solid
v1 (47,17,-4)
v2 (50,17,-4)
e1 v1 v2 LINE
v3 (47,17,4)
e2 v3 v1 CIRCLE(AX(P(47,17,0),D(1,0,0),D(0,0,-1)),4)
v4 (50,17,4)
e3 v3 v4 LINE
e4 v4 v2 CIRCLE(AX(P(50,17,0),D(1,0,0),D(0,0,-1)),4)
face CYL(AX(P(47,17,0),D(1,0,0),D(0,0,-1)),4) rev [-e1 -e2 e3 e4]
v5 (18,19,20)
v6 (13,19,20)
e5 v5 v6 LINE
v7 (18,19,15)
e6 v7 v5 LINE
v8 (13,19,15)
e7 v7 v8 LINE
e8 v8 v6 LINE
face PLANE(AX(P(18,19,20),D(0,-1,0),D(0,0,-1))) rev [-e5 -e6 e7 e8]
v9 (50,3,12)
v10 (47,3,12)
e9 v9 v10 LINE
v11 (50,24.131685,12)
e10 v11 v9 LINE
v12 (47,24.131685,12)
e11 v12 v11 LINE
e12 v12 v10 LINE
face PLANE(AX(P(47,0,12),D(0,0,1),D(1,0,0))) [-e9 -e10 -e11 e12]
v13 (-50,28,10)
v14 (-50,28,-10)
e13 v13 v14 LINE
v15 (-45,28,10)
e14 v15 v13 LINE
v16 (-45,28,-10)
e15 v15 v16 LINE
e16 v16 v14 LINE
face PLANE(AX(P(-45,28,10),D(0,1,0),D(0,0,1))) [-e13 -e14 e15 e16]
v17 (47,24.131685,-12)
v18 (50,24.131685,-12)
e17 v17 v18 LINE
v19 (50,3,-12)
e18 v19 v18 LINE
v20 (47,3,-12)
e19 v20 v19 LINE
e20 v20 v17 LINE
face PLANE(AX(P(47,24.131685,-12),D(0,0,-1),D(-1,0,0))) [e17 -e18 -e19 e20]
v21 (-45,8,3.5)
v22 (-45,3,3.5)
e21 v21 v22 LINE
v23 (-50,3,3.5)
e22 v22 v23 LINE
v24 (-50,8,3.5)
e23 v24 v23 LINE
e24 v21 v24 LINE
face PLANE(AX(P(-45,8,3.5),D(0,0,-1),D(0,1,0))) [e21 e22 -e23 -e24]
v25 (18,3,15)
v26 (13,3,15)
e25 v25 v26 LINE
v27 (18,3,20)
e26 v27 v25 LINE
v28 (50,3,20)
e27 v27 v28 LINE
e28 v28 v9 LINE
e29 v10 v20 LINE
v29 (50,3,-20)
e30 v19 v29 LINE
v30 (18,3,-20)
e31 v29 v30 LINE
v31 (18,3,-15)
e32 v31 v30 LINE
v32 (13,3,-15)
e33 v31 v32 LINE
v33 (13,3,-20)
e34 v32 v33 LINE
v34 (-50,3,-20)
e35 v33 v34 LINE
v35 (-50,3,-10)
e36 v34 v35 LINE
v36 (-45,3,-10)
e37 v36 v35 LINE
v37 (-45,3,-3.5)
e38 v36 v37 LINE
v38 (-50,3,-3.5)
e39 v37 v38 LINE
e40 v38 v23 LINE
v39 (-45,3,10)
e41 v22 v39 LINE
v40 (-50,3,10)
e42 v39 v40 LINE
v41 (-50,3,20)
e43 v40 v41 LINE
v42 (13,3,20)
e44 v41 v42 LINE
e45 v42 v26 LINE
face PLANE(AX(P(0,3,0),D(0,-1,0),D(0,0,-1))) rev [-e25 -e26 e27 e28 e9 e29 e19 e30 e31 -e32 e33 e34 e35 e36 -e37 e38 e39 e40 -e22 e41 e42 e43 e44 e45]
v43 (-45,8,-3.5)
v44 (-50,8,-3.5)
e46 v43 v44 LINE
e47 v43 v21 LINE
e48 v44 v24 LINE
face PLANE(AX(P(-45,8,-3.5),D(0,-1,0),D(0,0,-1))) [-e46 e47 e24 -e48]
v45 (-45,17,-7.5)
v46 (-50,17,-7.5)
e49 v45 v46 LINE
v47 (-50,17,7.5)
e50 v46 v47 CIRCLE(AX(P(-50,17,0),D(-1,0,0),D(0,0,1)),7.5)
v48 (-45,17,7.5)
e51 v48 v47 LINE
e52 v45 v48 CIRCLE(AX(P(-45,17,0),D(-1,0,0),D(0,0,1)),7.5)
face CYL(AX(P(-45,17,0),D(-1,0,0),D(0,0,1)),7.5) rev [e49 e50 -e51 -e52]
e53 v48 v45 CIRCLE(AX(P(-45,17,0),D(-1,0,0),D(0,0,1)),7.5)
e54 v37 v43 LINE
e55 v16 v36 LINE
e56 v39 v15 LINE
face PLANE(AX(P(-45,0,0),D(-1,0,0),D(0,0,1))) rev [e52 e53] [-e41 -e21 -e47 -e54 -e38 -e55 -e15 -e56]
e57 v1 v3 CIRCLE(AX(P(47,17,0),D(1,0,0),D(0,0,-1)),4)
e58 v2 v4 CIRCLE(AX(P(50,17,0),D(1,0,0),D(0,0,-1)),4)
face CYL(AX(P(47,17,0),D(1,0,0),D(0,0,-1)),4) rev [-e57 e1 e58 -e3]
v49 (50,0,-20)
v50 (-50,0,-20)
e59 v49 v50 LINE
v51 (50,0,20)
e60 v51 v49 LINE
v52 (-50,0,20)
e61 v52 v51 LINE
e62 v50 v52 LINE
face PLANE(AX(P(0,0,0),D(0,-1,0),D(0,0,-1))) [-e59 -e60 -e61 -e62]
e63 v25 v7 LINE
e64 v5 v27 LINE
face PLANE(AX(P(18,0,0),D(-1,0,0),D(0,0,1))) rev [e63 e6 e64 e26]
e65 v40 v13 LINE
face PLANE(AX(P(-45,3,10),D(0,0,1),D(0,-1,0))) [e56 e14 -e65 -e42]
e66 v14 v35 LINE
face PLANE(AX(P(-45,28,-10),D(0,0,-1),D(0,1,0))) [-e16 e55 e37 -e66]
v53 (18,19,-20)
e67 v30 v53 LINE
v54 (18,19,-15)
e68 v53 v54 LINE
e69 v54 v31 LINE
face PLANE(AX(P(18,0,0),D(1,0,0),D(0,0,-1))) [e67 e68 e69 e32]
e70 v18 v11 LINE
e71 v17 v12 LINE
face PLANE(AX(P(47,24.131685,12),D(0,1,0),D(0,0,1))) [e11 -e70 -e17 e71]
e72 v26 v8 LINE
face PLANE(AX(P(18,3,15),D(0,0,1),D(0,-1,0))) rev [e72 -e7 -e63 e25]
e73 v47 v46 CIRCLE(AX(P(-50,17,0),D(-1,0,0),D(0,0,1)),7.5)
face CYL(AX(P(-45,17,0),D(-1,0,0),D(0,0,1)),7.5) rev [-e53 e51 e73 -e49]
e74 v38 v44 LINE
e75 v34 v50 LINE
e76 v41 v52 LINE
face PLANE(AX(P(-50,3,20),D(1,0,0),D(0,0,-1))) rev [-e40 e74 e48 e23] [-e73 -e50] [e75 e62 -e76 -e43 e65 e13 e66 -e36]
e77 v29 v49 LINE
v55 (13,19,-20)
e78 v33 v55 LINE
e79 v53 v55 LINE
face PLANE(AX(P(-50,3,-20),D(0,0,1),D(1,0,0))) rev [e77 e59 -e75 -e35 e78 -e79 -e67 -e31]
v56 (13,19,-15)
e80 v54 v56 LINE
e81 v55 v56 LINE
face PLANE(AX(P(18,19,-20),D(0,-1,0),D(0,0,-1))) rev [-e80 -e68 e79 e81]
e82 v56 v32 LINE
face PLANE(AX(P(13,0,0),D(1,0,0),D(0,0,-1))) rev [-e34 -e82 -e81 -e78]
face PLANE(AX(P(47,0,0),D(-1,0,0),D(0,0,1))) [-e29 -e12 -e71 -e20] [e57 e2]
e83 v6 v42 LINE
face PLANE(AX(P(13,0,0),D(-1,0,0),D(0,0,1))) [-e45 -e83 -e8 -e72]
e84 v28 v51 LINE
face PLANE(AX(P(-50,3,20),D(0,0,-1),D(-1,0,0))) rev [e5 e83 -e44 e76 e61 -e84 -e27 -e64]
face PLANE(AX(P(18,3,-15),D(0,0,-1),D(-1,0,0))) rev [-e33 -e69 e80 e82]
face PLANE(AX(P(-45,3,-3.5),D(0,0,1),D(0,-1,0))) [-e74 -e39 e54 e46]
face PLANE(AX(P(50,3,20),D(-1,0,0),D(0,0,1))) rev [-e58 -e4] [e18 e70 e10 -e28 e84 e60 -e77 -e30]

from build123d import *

# Parameters (mm, degrees)
SKETCH1_W           = 100
SKETCH1_H           = 40
BOSS_EXTRUDE1_DEPTH = 3
SKETCH2_W           = 20
SKETCH2_H           = 25
SKETCH2_R           = 7.5
BOSS_EXTRUDE2_DEPTH = 5
SKETCH3_R           = 7.5
BOSS_EXTRUDE3_DEPTH = 5
SKETCH4_W           = 5
SKETCH4_H           = 16
BOSS_EXTRUDE4_DEPTH = 5
SKETCH7_W           = 24
SKETCH7_H           = 24.131684527
SKETCH7_R           = 4
BOSS_EXTRUDE5_DEPTH = 3
SKETCH9_W           = 8.913505449
SKETCH9_H           = 22.920442584
CUT_EXTRUDE3_DEPTH  = 47


with BuildPart() as part:
    # Sketch1 → Boss-Extrude1 (new body)
    with BuildSketch(Plane(origin=(0, 0, 0), x_dir=(1, 0, 0), z_dir=(0, 1, 0))):
        Rectangle(SKETCH1_W, SKETCH1_H)
    extrude(amount=BOSS_EXTRUDE1_DEPTH)

    # Sketch2 → Boss-Extrude2 (add)
    with BuildSketch(Plane(origin=(40, 0, 0), x_dir=(0, 0, -1), z_dir=(1, 0, 0))):
        with Locations((0, 15.5)):
            Rectangle(SKETCH2_W, SKETCH2_H)
        with Locations((0, 17)):
            Circle(SKETCH2_R, mode=Mode.SUBTRACT)
    extrude(amount=BOSS_EXTRUDE2_DEPTH)

    # Sketch3 → Boss-Extrude3 (add)
    with BuildSketch(Plane.ZY.offset(50)):
        Polygon((-10, 3), (-3.5, 3), (-3.5, 8), (3.5, 8), (3.5, 3), (10, 3), (10, 28), (-10, 28), align=None)
        with Locations(Location((0, 17, 0), (0, 0, 180))):
            Circle(SKETCH3_R, mode=Mode.SUBTRACT)
    extrude(amount=-BOSS_EXTRUDE3_DEPTH)

    # Sketch4 → Boss-Extrude4 (add)
    with BuildSketch(Plane(origin=(13, 0, 0), x_dir=(0, 0, -1), z_dir=(1, 0, 0))):
        with Locations((17.5, 11)):
            Rectangle(SKETCH4_W, SKETCH4_H)
        with Locations((-17.5, 11)):
            Rectangle(SKETCH4_W, SKETCH4_H)
    extrude(amount=BOSS_EXTRUDE4_DEPTH)

    # Sketch7 → Boss-Extrude5 (add)
    with BuildSketch(Plane(origin=(50, 0, 0), x_dir=(0, 0, -1), z_dir=(1, 0, 0))):
        with Locations((0, 12.065842264)):
            Rectangle(SKETCH7_W, SKETCH7_H)
        with Locations((0, 17)):
            Circle(SKETCH7_R, mode=Mode.SUBTRACT)
    extrude(amount=-BOSS_EXTRUDE5_DEPTH)

    # Sketch9 → Cut-Extrude3 (cut)
    with BuildSketch(Plane(origin=(0, 3, 0), x_dir=(1, 0, 0), z_dir=(0, 1, 0))):
        with Locations((40.747453483, 0)):
            Rectangle(SKETCH9_W, SKETCH9_H)
    extrude(amount=CUT_EXTRUDE3_DEPTH, mode=Mode.SUBTRACT)


solid = part.part
